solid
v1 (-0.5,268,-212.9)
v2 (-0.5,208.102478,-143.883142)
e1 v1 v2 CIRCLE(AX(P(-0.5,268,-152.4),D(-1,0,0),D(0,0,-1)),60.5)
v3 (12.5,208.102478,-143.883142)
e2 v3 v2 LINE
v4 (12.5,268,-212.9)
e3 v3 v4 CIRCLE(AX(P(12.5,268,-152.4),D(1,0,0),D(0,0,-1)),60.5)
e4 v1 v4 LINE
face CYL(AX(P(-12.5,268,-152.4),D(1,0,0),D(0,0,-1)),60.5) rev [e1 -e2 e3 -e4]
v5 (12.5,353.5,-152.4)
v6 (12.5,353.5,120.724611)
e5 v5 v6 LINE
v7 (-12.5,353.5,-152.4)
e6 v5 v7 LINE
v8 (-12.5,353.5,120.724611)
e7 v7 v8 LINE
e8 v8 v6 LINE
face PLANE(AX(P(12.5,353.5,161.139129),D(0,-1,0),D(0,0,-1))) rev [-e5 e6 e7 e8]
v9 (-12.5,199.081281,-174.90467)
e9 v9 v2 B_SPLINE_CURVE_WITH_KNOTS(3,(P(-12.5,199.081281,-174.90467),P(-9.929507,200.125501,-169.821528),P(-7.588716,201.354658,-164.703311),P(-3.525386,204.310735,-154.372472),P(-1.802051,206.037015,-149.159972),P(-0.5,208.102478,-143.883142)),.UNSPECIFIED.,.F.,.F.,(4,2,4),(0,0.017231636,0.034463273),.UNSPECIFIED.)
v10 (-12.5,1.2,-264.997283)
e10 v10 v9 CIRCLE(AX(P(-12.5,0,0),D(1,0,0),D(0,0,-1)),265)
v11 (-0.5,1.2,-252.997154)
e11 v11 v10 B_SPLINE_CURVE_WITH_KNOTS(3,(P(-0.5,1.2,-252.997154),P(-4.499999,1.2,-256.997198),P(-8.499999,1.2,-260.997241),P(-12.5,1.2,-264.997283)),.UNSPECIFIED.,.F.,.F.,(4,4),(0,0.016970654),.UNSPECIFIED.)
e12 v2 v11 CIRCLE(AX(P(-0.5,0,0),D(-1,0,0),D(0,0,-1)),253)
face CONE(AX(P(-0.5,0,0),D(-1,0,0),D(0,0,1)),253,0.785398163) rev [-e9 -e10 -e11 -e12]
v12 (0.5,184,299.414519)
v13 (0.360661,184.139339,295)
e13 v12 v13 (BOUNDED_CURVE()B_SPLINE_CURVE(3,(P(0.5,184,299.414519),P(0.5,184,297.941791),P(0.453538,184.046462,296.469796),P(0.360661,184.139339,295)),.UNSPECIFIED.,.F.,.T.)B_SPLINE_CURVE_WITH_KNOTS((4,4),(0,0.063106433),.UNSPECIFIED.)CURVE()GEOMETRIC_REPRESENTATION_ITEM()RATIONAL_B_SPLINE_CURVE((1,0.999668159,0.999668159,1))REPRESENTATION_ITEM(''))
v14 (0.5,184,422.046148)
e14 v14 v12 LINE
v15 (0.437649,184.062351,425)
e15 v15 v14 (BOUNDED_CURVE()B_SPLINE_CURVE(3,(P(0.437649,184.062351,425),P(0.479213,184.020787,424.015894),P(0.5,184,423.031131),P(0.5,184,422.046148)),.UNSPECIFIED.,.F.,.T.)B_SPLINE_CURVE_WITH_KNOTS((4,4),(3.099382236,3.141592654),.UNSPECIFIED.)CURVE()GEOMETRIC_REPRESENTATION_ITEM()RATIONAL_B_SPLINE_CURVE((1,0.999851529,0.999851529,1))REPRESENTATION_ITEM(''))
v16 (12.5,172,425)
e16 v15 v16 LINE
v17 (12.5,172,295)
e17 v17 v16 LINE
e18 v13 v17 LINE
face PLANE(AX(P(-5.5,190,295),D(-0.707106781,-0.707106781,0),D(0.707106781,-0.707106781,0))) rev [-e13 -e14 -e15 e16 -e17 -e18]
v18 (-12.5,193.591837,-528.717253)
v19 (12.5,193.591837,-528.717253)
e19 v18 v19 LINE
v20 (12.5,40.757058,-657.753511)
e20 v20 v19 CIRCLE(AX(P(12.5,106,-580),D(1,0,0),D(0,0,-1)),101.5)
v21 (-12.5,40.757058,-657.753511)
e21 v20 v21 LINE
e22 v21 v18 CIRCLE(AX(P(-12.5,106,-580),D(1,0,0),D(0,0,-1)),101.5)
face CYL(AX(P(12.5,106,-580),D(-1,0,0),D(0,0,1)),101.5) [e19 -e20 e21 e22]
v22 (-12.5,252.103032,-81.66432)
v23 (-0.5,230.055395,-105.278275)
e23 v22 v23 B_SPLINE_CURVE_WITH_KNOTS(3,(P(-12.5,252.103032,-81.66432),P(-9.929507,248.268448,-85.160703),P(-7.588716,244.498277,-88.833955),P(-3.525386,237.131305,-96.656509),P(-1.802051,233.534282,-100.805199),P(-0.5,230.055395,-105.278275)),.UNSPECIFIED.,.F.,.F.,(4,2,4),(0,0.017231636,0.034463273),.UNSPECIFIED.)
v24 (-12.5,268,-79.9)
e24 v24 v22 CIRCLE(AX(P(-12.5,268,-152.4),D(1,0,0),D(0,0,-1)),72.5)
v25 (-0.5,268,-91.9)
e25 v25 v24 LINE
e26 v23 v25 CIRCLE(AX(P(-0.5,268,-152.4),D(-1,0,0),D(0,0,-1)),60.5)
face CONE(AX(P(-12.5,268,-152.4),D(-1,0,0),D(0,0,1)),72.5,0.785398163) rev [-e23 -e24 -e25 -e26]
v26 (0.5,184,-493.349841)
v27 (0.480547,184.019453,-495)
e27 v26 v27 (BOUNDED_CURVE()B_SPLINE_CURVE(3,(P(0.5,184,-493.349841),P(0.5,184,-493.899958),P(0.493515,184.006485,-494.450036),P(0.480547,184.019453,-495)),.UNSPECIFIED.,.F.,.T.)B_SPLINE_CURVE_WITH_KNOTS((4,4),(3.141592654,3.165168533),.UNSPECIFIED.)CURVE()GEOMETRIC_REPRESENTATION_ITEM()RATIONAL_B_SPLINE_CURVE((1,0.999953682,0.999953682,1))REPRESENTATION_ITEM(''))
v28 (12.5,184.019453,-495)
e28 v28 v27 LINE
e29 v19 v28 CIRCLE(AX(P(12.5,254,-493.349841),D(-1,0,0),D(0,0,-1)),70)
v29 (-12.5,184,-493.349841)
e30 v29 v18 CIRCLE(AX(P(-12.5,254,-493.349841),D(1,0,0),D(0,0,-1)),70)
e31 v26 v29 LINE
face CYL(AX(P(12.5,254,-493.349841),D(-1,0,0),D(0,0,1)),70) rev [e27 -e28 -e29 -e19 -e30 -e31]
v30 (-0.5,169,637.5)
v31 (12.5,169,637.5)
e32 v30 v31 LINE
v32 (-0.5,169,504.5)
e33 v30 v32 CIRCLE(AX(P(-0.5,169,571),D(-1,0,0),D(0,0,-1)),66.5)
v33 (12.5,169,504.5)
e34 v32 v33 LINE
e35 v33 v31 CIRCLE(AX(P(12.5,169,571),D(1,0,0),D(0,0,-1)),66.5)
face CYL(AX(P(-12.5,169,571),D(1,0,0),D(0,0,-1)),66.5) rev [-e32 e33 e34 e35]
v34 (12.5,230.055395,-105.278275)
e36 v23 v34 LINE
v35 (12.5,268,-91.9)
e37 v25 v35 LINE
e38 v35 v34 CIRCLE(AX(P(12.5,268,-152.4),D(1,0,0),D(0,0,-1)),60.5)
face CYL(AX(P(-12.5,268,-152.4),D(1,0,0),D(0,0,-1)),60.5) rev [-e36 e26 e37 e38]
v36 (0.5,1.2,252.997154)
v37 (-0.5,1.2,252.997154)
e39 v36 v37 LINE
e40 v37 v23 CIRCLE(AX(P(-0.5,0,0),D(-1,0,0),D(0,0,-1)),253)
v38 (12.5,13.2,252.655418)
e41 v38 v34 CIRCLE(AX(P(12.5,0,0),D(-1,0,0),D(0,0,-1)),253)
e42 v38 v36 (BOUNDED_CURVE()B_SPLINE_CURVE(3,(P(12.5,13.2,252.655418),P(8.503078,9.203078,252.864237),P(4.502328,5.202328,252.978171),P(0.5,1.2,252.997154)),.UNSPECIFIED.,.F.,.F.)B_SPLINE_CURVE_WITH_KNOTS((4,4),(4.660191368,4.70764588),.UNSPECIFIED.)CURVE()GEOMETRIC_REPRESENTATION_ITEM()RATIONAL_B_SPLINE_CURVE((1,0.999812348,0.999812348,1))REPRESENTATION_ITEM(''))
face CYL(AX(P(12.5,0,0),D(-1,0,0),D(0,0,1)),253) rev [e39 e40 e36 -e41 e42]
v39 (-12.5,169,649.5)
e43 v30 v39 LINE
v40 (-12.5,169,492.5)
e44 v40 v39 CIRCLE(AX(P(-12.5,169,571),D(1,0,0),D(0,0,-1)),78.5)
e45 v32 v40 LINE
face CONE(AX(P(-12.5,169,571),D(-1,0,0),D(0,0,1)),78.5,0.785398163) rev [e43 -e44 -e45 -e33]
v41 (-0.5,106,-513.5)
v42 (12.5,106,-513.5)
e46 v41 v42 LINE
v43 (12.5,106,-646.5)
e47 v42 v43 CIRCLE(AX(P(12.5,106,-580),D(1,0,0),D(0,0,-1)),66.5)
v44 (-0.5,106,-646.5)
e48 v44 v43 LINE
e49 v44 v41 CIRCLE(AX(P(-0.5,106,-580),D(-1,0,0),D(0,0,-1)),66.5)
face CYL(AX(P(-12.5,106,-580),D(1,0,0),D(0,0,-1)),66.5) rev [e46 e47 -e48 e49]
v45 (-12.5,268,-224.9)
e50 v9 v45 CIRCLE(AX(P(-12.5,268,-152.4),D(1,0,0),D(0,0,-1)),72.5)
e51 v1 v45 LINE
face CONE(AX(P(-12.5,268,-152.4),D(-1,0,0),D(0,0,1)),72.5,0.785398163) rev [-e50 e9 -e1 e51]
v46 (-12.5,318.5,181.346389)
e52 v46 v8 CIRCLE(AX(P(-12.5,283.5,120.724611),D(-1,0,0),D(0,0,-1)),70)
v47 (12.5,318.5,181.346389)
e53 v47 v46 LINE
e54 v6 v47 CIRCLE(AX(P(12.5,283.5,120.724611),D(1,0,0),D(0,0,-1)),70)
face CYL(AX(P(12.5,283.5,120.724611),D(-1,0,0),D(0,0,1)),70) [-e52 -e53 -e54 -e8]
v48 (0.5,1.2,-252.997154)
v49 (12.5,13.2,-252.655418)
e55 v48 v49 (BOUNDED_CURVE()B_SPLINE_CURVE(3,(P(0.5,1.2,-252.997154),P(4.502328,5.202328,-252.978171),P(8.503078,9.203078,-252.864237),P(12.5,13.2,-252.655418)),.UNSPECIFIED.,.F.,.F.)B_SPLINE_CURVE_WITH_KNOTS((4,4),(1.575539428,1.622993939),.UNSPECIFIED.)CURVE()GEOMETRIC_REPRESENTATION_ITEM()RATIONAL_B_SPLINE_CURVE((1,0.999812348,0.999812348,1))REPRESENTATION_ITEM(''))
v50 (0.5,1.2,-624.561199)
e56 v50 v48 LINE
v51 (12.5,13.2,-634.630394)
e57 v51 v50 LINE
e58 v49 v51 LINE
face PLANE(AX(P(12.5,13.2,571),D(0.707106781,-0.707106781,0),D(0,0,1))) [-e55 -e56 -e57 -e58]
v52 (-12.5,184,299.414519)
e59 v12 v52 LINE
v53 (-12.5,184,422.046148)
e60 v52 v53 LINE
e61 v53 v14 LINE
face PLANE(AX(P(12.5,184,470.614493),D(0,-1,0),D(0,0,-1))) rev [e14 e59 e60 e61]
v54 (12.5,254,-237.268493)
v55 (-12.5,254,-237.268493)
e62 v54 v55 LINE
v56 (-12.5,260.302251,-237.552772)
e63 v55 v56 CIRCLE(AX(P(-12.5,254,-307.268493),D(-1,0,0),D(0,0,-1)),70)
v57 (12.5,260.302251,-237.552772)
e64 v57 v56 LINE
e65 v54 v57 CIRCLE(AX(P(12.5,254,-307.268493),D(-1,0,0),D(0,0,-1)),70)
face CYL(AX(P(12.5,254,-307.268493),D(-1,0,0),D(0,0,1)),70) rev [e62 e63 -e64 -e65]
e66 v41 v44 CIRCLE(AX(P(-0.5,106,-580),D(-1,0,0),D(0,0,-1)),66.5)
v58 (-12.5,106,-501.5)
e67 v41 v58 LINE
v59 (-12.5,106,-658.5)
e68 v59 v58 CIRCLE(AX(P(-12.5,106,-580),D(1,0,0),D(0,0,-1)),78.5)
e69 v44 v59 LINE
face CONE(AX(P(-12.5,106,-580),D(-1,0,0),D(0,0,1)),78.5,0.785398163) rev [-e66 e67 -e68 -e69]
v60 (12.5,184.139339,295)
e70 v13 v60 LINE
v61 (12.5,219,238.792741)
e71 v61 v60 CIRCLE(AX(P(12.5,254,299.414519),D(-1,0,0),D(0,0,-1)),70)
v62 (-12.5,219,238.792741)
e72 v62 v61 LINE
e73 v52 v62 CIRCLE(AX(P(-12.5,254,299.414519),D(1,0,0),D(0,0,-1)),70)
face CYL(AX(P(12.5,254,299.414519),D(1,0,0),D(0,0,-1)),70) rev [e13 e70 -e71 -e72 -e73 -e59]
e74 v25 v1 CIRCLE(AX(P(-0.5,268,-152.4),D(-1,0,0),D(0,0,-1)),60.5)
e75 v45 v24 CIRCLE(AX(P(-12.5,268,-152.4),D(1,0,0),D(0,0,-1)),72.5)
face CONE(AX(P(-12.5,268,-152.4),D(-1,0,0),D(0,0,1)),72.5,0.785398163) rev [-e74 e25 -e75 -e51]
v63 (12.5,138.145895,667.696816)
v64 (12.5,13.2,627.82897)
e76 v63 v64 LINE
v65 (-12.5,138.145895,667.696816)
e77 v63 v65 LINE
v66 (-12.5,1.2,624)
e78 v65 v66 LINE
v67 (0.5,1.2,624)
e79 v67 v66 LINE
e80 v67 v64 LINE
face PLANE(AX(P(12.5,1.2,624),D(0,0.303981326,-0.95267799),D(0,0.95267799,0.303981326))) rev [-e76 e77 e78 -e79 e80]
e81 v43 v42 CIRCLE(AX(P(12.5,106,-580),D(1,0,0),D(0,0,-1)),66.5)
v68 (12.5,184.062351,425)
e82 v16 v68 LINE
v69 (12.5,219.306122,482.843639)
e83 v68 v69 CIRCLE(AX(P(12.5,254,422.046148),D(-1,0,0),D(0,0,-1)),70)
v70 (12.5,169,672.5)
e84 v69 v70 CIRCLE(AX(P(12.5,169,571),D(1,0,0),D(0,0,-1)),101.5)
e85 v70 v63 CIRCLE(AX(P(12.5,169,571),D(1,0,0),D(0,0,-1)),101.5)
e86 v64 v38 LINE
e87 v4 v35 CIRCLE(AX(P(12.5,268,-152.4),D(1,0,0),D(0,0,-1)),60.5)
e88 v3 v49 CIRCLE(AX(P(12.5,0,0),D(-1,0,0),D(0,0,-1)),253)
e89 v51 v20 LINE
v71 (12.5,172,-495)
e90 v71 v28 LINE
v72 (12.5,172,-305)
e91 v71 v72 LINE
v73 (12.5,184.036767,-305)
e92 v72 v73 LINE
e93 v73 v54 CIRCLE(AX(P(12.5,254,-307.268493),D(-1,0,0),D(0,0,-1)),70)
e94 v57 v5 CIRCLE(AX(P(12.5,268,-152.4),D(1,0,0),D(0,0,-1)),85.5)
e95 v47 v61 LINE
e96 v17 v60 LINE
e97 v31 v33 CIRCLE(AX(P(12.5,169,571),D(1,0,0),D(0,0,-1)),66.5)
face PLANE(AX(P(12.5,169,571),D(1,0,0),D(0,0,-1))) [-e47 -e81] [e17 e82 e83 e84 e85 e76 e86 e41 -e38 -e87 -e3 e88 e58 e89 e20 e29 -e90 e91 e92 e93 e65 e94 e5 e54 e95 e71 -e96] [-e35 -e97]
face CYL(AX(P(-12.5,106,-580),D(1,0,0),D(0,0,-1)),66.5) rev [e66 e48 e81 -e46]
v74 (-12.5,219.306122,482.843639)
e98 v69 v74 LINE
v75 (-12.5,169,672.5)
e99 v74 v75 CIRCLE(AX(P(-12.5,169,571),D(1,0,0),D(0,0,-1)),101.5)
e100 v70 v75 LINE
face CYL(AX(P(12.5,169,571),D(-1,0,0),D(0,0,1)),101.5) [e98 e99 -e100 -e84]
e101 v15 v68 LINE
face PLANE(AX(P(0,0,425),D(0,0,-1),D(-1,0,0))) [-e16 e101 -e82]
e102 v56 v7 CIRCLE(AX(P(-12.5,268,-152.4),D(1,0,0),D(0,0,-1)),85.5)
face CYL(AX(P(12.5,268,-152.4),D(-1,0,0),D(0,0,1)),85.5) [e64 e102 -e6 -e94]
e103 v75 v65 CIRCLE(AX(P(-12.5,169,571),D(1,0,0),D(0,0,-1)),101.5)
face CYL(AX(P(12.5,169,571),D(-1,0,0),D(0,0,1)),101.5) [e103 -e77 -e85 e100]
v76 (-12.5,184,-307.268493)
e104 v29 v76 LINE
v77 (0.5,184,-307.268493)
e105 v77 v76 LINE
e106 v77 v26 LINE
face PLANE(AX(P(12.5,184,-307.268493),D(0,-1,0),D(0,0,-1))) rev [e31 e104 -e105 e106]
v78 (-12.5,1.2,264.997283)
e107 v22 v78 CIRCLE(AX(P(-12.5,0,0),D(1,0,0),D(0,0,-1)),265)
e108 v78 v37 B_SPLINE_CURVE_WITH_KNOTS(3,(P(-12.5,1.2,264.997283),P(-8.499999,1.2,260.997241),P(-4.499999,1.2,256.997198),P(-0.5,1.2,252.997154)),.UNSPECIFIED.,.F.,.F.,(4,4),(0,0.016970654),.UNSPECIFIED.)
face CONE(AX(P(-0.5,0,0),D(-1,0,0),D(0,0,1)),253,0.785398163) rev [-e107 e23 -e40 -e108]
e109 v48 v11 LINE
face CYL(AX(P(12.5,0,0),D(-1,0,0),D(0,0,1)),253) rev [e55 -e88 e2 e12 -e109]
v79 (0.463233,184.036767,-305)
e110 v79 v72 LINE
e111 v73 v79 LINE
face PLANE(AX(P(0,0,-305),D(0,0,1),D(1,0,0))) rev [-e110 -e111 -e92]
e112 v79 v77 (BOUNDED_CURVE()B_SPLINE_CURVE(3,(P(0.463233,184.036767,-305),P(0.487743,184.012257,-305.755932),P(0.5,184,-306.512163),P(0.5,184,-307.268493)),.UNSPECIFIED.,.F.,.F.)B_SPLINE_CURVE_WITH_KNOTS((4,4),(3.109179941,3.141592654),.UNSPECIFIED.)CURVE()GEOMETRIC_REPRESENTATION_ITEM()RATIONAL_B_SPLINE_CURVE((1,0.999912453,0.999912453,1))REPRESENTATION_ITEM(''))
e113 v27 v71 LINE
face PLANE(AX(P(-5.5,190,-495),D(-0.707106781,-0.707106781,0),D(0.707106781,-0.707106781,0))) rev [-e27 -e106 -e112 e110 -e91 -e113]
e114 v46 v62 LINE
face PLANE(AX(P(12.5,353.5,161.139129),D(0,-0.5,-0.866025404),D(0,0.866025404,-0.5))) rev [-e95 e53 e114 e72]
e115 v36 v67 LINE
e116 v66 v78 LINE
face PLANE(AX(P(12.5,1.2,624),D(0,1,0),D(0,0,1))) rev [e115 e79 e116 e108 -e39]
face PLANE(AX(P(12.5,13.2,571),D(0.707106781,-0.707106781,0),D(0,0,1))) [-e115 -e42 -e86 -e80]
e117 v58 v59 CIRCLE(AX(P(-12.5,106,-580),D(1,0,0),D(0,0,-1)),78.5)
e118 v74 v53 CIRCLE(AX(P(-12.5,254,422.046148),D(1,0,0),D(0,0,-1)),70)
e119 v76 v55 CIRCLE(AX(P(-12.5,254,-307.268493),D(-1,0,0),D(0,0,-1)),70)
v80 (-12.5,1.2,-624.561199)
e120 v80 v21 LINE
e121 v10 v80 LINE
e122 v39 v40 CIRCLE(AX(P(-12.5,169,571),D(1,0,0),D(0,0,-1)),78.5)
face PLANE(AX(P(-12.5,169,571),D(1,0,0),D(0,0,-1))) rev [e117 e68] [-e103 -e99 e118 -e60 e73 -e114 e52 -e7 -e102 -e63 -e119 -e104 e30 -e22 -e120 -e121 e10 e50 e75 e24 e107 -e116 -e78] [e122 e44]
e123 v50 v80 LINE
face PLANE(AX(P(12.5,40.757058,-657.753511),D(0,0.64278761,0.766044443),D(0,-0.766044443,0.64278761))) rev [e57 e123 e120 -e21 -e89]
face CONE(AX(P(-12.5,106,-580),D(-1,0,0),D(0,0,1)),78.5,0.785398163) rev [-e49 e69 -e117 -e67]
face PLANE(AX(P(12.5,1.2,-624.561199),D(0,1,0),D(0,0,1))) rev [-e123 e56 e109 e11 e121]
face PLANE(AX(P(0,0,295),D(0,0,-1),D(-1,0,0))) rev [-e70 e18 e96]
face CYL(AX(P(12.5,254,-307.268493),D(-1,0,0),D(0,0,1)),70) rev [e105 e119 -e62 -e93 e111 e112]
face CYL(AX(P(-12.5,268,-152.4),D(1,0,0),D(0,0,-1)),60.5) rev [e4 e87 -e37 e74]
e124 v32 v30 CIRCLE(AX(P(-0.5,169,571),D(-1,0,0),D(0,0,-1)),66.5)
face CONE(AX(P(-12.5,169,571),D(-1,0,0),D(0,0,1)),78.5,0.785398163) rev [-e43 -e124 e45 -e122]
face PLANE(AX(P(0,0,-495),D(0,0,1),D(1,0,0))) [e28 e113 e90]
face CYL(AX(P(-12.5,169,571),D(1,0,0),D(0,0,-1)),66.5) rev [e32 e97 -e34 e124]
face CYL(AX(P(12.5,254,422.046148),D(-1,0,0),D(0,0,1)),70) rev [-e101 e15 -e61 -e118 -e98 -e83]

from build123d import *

# Parameters (mm, degrees)
BOSS_EXTRUDE1_DEPTH     = 12.5
CUT_EXTRUDE1_DEPTH      = 768.828594154
CUT_EXTRUDE1_DEPTH_BACK = 768.828594154
SKETCH2_R               = 60.5
SKETCH2_R_2             = 66.5
FILLET1_R               = 70
CHAMFER1_SIZE           = 12
CHAMFER2_SIZE           = 12
CUT_EXTRUDE2_DEPTH      = 65
CUT_EXTRUDE3_DEPTH      = 95


with BuildPart() as part:
    # Sketch1 → Boss-Extrude1 (new, symmetric)
    with BuildSketch(Plane(origin=(0, 0, 0), x_dir=(0, 0, -1), z_dir=(1, 0, 0))):
        with BuildLine():
            Line((-161.139129372, 353.5), (152.4, 353.5))
            ThreePointArc((152.4, 353.5), (215.520549571, 325.671884154), (237.552772458, 260.302250804))
            ThreePointArc((237.552772458, 260.302250804), (255.590849676, 206.783252739), (307.268492599, 184))
            Line((307.268492599, 184), (515.051943832, 184))
            ThreePointArc((515.051943832, 184), (651.90709321, 177.635326105), (657.753510977, 40.757057617))
            Line((657.753510977, 40.757057617), (624.56119852, 1.2))
            Line((624.56119852, 1.2), (252.997154134, 1.2))
            ThreePointArc((252.997154134, 1.2), (0, 253), (-252.997154134, 1.2))
            Line((-252.997154134, 1.2), (-624, 1.2))
            Line((-624, 1.2), (-667.696816027, 138.145895408))
            ThreePointArc((-667.696816027, 138.145895408), (-594.001115997, 267.859489493), (-470.614493078, 184))
            Line((-470.614493078, 184), (-259, 184))
            Line((-259, 184), (-161.139129372, 353.5))
        make_face()
    extrude(amount=BOSS_EXTRUDE1_DEPTH, both=True)

    # Sketch2 → Cut-Extrude1 (cut, two sides: drawn at the far end of the back side and taken through both)
    with BuildSketch(Plane(origin=(0, 0, 0), x_dir=(0, 0, -1), z_dir=(1, 0, 0)).offset(-CUT_EXTRUDE1_DEPTH_BACK)):
        with Locations((152.4, 268)):
            Circle(SKETCH2_R)
        with Locations((-571, 169)):
            Circle(SKETCH2_R_2)
        with Locations((580, 106)):
            Circle(SKETCH2_R_2)
    extrude(amount=CUT_EXTRUDE1_DEPTH + CUT_EXTRUDE1_DEPTH_BACK, mode=Mode.SUBTRACT)

    # Fillet1
    fillet1_edges = [part.edges().sort_by_distance(p)[0] for p in [
        (0, 184, 470.614493078),
        (0, 184, 259),
        (0, 353.5, 161.139129372),
        (0, 184, -515.051943832),
    ]]
    fillet(fillet1_edges, radius=FILLET1_R)

    # Chamfer1
    chamfer1_edges = [part.edges().sort_by_distance(p)[0] for p in [
        (12.5, 1.2, 438.498577067),
        (12.5, 1.2, -438.779176327),
    ]]
    chamfer(chamfer1_edges, length=CHAMFER1_SIZE)

    # Chamfer2
    chamfer2_edges = [part.edges().sort_by_distance(p)[0] for p in [
        (-12.5, 213.213707904, 136.194400626),
        (-12.5, 118.018425376, -223.787066811),
        (-12.5, 320.591390839, -182.306447626),
        (-12.5, 169, 637.5),
        (-12.5, 106, -513.5),
    ]]
    chamfer(chamfer2_edges, length=CHAMFER2_SIZE)

    # Sketch3 → Cut-Extrude2 (cut, symmetric)
    with BuildSketch(Plane.XY.offset(360)):
        Polygon((-5.5, 190), (12.5, 172), (12.5, 190), align=None)
    extrude(amount=CUT_EXTRUDE2_DEPTH, both=True, mode=Mode.SUBTRACT)

    # Sketch4 → Cut-Extrude3 (cut, symmetric)
    with BuildSketch(Plane.XY.offset(-400)):
        Polygon((12.5, 190), (-5.5, 190), (12.5, 172), align=None)
    extrude(amount=CUT_EXTRUDE3_DEPTH, both=True, mode=Mode.SUBTRACT)


solid = part.part
